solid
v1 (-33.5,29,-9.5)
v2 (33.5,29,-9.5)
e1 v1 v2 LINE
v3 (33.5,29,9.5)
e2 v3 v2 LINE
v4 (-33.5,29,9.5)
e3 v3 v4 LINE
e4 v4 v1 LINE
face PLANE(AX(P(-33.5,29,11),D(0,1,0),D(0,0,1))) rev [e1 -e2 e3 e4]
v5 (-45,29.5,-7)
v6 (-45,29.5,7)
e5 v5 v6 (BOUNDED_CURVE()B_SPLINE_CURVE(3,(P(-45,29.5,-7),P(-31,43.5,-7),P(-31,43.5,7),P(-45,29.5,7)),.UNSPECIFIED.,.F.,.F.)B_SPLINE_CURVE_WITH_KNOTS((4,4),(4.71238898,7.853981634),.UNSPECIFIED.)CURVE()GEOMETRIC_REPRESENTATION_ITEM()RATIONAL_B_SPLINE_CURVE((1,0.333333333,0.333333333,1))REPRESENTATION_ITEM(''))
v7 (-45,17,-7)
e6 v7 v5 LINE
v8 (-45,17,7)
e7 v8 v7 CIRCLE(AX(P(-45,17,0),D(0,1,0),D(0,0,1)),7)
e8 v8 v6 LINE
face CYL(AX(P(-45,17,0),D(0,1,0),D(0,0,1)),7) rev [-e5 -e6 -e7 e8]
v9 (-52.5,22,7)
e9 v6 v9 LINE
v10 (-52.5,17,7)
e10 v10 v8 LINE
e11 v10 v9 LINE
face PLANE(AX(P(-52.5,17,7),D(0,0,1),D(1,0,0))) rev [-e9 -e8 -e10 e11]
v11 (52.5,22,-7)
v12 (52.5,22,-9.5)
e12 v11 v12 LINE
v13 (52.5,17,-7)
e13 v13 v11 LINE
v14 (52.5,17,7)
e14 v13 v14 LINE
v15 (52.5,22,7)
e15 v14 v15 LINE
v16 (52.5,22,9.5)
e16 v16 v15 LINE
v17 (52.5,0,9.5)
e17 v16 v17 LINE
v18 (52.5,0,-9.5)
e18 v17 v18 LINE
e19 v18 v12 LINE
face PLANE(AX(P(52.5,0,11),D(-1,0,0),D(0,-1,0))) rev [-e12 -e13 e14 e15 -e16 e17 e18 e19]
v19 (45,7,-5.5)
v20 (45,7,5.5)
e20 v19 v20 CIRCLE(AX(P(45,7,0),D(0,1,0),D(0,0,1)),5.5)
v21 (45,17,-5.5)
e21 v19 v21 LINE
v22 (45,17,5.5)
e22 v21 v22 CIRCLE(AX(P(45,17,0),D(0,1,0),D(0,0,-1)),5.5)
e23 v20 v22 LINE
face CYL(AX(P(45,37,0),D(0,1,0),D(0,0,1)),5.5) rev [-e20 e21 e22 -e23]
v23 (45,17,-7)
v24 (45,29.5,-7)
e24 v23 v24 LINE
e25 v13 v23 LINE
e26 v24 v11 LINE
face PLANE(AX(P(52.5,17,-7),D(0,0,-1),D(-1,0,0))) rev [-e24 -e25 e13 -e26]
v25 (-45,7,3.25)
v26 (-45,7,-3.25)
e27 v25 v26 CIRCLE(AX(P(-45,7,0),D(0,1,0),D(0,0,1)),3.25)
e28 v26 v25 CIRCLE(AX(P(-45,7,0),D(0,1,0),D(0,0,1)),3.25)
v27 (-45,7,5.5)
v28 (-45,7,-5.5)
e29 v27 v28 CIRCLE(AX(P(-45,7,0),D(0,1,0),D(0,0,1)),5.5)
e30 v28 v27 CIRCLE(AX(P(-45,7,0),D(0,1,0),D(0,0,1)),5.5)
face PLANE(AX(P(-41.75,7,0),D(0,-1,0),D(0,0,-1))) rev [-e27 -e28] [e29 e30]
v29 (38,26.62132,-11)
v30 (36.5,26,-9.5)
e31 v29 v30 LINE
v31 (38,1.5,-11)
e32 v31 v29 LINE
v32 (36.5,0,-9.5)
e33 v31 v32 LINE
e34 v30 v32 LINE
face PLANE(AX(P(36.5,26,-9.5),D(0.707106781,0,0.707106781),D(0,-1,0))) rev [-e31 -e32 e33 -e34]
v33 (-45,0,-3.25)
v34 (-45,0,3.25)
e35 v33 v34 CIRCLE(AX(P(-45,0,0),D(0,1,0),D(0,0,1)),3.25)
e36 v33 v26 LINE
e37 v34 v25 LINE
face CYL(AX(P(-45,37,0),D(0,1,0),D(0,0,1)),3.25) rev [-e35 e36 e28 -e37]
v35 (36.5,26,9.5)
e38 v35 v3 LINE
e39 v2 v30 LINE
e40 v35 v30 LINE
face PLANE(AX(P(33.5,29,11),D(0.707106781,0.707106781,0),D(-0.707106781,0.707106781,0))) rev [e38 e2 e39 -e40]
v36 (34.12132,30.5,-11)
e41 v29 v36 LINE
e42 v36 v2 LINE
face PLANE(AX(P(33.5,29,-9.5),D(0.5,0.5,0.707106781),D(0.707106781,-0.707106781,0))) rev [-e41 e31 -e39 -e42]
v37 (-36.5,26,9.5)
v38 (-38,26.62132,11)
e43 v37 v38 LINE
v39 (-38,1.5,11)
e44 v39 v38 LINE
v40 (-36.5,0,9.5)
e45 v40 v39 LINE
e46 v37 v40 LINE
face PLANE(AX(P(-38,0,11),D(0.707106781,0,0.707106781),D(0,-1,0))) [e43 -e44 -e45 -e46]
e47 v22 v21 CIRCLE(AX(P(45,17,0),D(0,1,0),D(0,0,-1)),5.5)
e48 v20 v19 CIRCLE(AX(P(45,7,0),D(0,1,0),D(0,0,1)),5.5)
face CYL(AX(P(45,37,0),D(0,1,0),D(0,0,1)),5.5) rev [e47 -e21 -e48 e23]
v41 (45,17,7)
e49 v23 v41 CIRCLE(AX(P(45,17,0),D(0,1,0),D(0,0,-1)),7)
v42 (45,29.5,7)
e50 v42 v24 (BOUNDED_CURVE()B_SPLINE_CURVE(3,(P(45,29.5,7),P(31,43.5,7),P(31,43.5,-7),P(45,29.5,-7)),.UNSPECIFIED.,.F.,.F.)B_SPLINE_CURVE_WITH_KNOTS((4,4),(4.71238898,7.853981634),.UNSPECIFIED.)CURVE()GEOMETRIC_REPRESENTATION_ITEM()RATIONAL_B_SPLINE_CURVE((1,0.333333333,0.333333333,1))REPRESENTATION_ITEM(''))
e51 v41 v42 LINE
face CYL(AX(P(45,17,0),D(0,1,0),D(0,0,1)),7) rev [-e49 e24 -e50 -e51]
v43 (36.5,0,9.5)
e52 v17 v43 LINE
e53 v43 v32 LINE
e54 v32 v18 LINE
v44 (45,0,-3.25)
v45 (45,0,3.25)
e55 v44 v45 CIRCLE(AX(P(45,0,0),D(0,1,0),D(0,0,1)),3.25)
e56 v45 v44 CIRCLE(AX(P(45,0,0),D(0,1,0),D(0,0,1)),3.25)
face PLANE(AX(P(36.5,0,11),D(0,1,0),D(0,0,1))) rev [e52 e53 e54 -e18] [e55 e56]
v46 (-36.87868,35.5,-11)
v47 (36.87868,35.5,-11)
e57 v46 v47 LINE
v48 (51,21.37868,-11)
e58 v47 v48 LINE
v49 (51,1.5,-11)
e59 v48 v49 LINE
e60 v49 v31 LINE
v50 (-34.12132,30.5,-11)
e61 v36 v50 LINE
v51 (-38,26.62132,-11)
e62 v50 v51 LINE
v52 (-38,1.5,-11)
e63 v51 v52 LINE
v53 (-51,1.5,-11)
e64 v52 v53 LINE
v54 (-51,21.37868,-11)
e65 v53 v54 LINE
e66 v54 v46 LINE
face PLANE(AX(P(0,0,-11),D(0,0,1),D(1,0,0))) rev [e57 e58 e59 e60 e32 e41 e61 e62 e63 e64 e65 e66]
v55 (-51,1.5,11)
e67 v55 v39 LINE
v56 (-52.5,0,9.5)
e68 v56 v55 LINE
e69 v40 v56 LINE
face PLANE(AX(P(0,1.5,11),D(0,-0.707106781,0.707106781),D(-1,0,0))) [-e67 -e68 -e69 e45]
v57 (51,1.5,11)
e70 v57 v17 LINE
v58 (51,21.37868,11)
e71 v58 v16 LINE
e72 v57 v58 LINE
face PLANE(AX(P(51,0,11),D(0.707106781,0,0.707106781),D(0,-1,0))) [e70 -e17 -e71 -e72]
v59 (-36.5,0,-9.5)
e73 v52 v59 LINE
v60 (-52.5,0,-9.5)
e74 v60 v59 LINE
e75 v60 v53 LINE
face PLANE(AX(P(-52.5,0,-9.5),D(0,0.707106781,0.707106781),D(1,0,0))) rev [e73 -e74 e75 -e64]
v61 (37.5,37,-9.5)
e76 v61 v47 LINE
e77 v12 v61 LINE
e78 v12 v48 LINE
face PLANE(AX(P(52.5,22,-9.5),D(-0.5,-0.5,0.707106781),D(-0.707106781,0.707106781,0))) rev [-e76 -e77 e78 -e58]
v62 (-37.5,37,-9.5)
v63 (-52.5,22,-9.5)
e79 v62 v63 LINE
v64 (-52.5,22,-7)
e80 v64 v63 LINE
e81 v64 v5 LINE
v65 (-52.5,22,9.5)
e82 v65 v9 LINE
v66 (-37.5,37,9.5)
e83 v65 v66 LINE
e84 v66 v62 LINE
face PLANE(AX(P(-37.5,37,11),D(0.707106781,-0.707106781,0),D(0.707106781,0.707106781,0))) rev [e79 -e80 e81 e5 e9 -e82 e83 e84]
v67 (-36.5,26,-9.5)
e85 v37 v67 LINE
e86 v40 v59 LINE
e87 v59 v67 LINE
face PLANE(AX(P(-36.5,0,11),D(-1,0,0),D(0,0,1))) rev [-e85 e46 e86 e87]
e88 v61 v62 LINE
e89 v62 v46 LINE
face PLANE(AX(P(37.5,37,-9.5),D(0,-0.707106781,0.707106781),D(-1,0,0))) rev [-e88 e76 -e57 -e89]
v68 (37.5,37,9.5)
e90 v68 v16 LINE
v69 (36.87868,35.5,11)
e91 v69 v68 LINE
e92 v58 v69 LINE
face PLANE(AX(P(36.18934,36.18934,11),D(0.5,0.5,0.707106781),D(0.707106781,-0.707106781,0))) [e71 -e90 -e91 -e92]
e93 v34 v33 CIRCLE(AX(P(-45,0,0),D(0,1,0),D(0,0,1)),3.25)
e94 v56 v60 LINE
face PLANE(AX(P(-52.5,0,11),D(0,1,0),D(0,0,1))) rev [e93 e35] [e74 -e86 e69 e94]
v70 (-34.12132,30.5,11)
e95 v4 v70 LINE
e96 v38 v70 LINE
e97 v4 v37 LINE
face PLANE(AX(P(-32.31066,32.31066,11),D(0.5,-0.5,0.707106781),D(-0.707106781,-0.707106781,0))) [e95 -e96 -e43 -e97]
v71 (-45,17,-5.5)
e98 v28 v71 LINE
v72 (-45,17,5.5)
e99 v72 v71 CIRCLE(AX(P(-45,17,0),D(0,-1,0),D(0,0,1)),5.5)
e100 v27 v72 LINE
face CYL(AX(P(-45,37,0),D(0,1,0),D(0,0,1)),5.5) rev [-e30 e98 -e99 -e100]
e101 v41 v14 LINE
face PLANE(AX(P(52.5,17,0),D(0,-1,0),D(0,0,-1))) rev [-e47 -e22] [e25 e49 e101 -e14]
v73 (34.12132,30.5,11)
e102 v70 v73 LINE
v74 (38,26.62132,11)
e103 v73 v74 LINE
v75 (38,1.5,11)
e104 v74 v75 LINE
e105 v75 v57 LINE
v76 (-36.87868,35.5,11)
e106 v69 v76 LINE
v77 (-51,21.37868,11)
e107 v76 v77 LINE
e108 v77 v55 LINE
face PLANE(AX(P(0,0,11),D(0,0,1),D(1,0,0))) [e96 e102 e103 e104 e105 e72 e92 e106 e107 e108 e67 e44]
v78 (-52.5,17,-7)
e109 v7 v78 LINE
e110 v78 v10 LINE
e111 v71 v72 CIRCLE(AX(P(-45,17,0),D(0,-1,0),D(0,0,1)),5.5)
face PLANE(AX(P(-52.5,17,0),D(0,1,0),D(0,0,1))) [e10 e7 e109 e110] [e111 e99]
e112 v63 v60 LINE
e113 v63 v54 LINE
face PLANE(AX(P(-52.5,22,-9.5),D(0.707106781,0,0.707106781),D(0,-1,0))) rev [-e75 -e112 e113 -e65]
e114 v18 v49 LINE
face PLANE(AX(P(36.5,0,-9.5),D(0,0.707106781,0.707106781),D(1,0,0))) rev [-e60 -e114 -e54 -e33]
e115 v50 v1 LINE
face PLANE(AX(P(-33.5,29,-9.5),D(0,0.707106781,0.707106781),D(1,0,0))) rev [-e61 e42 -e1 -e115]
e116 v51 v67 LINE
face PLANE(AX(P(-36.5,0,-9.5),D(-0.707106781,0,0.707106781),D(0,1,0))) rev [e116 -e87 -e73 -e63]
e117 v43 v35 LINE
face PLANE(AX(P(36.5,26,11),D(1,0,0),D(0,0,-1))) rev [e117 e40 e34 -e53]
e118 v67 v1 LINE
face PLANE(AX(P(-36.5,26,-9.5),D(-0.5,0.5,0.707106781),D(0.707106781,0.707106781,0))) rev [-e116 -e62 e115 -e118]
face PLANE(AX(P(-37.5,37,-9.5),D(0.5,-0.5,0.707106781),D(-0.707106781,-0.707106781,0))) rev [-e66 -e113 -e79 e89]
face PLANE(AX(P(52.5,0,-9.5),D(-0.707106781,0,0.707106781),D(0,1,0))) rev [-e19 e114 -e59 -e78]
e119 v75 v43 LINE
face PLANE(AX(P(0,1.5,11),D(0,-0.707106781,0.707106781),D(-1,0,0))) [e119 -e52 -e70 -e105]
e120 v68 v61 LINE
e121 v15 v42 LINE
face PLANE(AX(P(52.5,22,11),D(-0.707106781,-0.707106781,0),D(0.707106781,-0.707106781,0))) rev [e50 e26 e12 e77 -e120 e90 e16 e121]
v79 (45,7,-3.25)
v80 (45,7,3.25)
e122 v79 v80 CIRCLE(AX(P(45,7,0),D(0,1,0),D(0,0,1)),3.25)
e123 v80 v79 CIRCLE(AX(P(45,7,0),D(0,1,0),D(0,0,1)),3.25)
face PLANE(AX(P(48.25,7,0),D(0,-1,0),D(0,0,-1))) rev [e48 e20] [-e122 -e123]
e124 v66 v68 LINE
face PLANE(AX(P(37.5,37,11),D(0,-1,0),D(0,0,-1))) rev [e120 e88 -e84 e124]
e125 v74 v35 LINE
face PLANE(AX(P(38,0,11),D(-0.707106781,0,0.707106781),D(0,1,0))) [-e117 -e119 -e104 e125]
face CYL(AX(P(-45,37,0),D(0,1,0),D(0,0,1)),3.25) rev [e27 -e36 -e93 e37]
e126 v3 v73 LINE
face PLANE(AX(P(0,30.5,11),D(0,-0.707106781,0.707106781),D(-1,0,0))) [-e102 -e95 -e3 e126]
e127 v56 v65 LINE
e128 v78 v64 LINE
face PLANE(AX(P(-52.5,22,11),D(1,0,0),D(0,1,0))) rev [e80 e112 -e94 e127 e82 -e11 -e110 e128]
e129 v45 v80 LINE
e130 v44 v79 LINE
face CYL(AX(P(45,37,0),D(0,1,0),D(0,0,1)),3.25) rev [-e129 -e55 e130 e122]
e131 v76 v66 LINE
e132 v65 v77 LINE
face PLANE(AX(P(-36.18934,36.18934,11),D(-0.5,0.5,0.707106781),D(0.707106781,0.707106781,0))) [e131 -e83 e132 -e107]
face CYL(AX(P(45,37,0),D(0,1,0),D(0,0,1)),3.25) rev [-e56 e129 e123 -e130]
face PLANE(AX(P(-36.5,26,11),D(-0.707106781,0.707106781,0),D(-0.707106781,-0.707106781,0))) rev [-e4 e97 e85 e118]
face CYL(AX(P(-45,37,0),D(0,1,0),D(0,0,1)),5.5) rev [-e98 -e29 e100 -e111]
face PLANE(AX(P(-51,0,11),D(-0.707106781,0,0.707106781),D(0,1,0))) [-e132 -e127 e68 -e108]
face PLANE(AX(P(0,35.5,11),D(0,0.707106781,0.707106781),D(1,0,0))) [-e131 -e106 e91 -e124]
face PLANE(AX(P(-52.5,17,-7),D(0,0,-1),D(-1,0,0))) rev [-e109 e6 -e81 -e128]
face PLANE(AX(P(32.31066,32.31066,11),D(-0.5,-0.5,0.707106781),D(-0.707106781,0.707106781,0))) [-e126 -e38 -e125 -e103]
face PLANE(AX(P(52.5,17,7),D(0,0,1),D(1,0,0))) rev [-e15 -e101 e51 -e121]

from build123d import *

# Parameters (mm, degrees)
EXTRUDE_1_DEPTH              = 11
HOLE_WIZARD_M6_1_D           = 6.5
HOLE_WIZARD_M6_1_CBORE_D     = 11
HOLE_WIZARD_M6_1_CBORE_DEPTH = 30
CUT_EXTRUDE_1_DEPTH          = 20
CHAMFER_1_SIZE               = 1.5


with BuildPart() as part:
    # 草图1 → 凸台-拉伸1 (new, symmetric)
    with BuildSketch(Plane.XY):
        Polygon((-52.5, 0), (-36.5, 0), (-36.5, 26), (-33.5, 29), (33.5, 29), (36.5, 26), (36.5, 0), (52.5, 0), (52.5, 22), (37.5, 37), (-37.5, 37), (-52.5, 22), align=None)
    extrude(amount=EXTRUDE_1_DEPTH, both=True)

    # M6 六角凹头螺钉的柱形沉头孔1 (through all)
    with Locations(Plane(origin=(0, 37, 0), x_dir=(1, 0, 0), z_dir=(0, 1, 0))):
        with Locations((-45, 0), (45, 0)):
            CounterBoreHole(HOLE_WIZARD_M6_1_D / 2, HOLE_WIZARD_M6_1_CBORE_D / 2, HOLE_WIZARD_M6_1_CBORE_DEPTH)

    # 草图4 → 切除-拉伸1 (cut)
    with BuildSketch(Plane(origin=(0, 37, 0), x_dir=(1, 0, 0), z_dir=(0, 1, 0))):
        with BuildLine():
            Line((-52.5, 7), (-45, 7))
            ThreePointArc((-45, 7), (-38, 0), (-45, -7))
            Line((-45, -7), (-52.5, -7))
            ThreePointArc((-52.5, -7), (-59.5, 0), (-52.5, 7))
        make_face()
        with BuildLine():
            Line((52.5, 7), (45, 7))
            ThreePointArc((45, 7), (38, 0), (45, -7))
            Line((45, -7), (52.5, -7))
            ThreePointArc((52.5, -7), (59.5, 0), (52.5, 7))
        make_face()
    extrude(amount=-CUT_EXTRUDE_1_DEPTH, mode=Mode.SUBTRACT)

    # 倒角1
    chamfer_1_edges = [part.edges().sort_by_distance(p)[0] for p in [
        (-36.5, 13, 11),
        (-45, 29.5, -11),
        (0, 37, -11),
        (45, 29.5, -11),
        (52.5, 11, -11),
        (44.5, 0, -11),
        (36.5, 13, -11),
        (-35, 27.5, 11),
        (35, 27.5, -11),
        (0, 29, -11),
        (-35, 27.5, -11),
        (-36.5, 13, -11),
        (-44.5, 0, -11),
        (-52.5, 11, -11),
        (0, 29, 11),
        (35, 27.5, 11),
        (36.5, 13, 11),
        (44.5, 0, 11),
        (52.5, 11, 11),
        (45, 29.5, 11),
        (0, 37, 11),
        (-45, 29.5, 11),
        (-52.5, 11, 11),
        (-44.5, 0, 11),
    ]]
    chamfer(chamfer_1_edges, length=CHAMFER_1_SIZE)


solid = part.part
